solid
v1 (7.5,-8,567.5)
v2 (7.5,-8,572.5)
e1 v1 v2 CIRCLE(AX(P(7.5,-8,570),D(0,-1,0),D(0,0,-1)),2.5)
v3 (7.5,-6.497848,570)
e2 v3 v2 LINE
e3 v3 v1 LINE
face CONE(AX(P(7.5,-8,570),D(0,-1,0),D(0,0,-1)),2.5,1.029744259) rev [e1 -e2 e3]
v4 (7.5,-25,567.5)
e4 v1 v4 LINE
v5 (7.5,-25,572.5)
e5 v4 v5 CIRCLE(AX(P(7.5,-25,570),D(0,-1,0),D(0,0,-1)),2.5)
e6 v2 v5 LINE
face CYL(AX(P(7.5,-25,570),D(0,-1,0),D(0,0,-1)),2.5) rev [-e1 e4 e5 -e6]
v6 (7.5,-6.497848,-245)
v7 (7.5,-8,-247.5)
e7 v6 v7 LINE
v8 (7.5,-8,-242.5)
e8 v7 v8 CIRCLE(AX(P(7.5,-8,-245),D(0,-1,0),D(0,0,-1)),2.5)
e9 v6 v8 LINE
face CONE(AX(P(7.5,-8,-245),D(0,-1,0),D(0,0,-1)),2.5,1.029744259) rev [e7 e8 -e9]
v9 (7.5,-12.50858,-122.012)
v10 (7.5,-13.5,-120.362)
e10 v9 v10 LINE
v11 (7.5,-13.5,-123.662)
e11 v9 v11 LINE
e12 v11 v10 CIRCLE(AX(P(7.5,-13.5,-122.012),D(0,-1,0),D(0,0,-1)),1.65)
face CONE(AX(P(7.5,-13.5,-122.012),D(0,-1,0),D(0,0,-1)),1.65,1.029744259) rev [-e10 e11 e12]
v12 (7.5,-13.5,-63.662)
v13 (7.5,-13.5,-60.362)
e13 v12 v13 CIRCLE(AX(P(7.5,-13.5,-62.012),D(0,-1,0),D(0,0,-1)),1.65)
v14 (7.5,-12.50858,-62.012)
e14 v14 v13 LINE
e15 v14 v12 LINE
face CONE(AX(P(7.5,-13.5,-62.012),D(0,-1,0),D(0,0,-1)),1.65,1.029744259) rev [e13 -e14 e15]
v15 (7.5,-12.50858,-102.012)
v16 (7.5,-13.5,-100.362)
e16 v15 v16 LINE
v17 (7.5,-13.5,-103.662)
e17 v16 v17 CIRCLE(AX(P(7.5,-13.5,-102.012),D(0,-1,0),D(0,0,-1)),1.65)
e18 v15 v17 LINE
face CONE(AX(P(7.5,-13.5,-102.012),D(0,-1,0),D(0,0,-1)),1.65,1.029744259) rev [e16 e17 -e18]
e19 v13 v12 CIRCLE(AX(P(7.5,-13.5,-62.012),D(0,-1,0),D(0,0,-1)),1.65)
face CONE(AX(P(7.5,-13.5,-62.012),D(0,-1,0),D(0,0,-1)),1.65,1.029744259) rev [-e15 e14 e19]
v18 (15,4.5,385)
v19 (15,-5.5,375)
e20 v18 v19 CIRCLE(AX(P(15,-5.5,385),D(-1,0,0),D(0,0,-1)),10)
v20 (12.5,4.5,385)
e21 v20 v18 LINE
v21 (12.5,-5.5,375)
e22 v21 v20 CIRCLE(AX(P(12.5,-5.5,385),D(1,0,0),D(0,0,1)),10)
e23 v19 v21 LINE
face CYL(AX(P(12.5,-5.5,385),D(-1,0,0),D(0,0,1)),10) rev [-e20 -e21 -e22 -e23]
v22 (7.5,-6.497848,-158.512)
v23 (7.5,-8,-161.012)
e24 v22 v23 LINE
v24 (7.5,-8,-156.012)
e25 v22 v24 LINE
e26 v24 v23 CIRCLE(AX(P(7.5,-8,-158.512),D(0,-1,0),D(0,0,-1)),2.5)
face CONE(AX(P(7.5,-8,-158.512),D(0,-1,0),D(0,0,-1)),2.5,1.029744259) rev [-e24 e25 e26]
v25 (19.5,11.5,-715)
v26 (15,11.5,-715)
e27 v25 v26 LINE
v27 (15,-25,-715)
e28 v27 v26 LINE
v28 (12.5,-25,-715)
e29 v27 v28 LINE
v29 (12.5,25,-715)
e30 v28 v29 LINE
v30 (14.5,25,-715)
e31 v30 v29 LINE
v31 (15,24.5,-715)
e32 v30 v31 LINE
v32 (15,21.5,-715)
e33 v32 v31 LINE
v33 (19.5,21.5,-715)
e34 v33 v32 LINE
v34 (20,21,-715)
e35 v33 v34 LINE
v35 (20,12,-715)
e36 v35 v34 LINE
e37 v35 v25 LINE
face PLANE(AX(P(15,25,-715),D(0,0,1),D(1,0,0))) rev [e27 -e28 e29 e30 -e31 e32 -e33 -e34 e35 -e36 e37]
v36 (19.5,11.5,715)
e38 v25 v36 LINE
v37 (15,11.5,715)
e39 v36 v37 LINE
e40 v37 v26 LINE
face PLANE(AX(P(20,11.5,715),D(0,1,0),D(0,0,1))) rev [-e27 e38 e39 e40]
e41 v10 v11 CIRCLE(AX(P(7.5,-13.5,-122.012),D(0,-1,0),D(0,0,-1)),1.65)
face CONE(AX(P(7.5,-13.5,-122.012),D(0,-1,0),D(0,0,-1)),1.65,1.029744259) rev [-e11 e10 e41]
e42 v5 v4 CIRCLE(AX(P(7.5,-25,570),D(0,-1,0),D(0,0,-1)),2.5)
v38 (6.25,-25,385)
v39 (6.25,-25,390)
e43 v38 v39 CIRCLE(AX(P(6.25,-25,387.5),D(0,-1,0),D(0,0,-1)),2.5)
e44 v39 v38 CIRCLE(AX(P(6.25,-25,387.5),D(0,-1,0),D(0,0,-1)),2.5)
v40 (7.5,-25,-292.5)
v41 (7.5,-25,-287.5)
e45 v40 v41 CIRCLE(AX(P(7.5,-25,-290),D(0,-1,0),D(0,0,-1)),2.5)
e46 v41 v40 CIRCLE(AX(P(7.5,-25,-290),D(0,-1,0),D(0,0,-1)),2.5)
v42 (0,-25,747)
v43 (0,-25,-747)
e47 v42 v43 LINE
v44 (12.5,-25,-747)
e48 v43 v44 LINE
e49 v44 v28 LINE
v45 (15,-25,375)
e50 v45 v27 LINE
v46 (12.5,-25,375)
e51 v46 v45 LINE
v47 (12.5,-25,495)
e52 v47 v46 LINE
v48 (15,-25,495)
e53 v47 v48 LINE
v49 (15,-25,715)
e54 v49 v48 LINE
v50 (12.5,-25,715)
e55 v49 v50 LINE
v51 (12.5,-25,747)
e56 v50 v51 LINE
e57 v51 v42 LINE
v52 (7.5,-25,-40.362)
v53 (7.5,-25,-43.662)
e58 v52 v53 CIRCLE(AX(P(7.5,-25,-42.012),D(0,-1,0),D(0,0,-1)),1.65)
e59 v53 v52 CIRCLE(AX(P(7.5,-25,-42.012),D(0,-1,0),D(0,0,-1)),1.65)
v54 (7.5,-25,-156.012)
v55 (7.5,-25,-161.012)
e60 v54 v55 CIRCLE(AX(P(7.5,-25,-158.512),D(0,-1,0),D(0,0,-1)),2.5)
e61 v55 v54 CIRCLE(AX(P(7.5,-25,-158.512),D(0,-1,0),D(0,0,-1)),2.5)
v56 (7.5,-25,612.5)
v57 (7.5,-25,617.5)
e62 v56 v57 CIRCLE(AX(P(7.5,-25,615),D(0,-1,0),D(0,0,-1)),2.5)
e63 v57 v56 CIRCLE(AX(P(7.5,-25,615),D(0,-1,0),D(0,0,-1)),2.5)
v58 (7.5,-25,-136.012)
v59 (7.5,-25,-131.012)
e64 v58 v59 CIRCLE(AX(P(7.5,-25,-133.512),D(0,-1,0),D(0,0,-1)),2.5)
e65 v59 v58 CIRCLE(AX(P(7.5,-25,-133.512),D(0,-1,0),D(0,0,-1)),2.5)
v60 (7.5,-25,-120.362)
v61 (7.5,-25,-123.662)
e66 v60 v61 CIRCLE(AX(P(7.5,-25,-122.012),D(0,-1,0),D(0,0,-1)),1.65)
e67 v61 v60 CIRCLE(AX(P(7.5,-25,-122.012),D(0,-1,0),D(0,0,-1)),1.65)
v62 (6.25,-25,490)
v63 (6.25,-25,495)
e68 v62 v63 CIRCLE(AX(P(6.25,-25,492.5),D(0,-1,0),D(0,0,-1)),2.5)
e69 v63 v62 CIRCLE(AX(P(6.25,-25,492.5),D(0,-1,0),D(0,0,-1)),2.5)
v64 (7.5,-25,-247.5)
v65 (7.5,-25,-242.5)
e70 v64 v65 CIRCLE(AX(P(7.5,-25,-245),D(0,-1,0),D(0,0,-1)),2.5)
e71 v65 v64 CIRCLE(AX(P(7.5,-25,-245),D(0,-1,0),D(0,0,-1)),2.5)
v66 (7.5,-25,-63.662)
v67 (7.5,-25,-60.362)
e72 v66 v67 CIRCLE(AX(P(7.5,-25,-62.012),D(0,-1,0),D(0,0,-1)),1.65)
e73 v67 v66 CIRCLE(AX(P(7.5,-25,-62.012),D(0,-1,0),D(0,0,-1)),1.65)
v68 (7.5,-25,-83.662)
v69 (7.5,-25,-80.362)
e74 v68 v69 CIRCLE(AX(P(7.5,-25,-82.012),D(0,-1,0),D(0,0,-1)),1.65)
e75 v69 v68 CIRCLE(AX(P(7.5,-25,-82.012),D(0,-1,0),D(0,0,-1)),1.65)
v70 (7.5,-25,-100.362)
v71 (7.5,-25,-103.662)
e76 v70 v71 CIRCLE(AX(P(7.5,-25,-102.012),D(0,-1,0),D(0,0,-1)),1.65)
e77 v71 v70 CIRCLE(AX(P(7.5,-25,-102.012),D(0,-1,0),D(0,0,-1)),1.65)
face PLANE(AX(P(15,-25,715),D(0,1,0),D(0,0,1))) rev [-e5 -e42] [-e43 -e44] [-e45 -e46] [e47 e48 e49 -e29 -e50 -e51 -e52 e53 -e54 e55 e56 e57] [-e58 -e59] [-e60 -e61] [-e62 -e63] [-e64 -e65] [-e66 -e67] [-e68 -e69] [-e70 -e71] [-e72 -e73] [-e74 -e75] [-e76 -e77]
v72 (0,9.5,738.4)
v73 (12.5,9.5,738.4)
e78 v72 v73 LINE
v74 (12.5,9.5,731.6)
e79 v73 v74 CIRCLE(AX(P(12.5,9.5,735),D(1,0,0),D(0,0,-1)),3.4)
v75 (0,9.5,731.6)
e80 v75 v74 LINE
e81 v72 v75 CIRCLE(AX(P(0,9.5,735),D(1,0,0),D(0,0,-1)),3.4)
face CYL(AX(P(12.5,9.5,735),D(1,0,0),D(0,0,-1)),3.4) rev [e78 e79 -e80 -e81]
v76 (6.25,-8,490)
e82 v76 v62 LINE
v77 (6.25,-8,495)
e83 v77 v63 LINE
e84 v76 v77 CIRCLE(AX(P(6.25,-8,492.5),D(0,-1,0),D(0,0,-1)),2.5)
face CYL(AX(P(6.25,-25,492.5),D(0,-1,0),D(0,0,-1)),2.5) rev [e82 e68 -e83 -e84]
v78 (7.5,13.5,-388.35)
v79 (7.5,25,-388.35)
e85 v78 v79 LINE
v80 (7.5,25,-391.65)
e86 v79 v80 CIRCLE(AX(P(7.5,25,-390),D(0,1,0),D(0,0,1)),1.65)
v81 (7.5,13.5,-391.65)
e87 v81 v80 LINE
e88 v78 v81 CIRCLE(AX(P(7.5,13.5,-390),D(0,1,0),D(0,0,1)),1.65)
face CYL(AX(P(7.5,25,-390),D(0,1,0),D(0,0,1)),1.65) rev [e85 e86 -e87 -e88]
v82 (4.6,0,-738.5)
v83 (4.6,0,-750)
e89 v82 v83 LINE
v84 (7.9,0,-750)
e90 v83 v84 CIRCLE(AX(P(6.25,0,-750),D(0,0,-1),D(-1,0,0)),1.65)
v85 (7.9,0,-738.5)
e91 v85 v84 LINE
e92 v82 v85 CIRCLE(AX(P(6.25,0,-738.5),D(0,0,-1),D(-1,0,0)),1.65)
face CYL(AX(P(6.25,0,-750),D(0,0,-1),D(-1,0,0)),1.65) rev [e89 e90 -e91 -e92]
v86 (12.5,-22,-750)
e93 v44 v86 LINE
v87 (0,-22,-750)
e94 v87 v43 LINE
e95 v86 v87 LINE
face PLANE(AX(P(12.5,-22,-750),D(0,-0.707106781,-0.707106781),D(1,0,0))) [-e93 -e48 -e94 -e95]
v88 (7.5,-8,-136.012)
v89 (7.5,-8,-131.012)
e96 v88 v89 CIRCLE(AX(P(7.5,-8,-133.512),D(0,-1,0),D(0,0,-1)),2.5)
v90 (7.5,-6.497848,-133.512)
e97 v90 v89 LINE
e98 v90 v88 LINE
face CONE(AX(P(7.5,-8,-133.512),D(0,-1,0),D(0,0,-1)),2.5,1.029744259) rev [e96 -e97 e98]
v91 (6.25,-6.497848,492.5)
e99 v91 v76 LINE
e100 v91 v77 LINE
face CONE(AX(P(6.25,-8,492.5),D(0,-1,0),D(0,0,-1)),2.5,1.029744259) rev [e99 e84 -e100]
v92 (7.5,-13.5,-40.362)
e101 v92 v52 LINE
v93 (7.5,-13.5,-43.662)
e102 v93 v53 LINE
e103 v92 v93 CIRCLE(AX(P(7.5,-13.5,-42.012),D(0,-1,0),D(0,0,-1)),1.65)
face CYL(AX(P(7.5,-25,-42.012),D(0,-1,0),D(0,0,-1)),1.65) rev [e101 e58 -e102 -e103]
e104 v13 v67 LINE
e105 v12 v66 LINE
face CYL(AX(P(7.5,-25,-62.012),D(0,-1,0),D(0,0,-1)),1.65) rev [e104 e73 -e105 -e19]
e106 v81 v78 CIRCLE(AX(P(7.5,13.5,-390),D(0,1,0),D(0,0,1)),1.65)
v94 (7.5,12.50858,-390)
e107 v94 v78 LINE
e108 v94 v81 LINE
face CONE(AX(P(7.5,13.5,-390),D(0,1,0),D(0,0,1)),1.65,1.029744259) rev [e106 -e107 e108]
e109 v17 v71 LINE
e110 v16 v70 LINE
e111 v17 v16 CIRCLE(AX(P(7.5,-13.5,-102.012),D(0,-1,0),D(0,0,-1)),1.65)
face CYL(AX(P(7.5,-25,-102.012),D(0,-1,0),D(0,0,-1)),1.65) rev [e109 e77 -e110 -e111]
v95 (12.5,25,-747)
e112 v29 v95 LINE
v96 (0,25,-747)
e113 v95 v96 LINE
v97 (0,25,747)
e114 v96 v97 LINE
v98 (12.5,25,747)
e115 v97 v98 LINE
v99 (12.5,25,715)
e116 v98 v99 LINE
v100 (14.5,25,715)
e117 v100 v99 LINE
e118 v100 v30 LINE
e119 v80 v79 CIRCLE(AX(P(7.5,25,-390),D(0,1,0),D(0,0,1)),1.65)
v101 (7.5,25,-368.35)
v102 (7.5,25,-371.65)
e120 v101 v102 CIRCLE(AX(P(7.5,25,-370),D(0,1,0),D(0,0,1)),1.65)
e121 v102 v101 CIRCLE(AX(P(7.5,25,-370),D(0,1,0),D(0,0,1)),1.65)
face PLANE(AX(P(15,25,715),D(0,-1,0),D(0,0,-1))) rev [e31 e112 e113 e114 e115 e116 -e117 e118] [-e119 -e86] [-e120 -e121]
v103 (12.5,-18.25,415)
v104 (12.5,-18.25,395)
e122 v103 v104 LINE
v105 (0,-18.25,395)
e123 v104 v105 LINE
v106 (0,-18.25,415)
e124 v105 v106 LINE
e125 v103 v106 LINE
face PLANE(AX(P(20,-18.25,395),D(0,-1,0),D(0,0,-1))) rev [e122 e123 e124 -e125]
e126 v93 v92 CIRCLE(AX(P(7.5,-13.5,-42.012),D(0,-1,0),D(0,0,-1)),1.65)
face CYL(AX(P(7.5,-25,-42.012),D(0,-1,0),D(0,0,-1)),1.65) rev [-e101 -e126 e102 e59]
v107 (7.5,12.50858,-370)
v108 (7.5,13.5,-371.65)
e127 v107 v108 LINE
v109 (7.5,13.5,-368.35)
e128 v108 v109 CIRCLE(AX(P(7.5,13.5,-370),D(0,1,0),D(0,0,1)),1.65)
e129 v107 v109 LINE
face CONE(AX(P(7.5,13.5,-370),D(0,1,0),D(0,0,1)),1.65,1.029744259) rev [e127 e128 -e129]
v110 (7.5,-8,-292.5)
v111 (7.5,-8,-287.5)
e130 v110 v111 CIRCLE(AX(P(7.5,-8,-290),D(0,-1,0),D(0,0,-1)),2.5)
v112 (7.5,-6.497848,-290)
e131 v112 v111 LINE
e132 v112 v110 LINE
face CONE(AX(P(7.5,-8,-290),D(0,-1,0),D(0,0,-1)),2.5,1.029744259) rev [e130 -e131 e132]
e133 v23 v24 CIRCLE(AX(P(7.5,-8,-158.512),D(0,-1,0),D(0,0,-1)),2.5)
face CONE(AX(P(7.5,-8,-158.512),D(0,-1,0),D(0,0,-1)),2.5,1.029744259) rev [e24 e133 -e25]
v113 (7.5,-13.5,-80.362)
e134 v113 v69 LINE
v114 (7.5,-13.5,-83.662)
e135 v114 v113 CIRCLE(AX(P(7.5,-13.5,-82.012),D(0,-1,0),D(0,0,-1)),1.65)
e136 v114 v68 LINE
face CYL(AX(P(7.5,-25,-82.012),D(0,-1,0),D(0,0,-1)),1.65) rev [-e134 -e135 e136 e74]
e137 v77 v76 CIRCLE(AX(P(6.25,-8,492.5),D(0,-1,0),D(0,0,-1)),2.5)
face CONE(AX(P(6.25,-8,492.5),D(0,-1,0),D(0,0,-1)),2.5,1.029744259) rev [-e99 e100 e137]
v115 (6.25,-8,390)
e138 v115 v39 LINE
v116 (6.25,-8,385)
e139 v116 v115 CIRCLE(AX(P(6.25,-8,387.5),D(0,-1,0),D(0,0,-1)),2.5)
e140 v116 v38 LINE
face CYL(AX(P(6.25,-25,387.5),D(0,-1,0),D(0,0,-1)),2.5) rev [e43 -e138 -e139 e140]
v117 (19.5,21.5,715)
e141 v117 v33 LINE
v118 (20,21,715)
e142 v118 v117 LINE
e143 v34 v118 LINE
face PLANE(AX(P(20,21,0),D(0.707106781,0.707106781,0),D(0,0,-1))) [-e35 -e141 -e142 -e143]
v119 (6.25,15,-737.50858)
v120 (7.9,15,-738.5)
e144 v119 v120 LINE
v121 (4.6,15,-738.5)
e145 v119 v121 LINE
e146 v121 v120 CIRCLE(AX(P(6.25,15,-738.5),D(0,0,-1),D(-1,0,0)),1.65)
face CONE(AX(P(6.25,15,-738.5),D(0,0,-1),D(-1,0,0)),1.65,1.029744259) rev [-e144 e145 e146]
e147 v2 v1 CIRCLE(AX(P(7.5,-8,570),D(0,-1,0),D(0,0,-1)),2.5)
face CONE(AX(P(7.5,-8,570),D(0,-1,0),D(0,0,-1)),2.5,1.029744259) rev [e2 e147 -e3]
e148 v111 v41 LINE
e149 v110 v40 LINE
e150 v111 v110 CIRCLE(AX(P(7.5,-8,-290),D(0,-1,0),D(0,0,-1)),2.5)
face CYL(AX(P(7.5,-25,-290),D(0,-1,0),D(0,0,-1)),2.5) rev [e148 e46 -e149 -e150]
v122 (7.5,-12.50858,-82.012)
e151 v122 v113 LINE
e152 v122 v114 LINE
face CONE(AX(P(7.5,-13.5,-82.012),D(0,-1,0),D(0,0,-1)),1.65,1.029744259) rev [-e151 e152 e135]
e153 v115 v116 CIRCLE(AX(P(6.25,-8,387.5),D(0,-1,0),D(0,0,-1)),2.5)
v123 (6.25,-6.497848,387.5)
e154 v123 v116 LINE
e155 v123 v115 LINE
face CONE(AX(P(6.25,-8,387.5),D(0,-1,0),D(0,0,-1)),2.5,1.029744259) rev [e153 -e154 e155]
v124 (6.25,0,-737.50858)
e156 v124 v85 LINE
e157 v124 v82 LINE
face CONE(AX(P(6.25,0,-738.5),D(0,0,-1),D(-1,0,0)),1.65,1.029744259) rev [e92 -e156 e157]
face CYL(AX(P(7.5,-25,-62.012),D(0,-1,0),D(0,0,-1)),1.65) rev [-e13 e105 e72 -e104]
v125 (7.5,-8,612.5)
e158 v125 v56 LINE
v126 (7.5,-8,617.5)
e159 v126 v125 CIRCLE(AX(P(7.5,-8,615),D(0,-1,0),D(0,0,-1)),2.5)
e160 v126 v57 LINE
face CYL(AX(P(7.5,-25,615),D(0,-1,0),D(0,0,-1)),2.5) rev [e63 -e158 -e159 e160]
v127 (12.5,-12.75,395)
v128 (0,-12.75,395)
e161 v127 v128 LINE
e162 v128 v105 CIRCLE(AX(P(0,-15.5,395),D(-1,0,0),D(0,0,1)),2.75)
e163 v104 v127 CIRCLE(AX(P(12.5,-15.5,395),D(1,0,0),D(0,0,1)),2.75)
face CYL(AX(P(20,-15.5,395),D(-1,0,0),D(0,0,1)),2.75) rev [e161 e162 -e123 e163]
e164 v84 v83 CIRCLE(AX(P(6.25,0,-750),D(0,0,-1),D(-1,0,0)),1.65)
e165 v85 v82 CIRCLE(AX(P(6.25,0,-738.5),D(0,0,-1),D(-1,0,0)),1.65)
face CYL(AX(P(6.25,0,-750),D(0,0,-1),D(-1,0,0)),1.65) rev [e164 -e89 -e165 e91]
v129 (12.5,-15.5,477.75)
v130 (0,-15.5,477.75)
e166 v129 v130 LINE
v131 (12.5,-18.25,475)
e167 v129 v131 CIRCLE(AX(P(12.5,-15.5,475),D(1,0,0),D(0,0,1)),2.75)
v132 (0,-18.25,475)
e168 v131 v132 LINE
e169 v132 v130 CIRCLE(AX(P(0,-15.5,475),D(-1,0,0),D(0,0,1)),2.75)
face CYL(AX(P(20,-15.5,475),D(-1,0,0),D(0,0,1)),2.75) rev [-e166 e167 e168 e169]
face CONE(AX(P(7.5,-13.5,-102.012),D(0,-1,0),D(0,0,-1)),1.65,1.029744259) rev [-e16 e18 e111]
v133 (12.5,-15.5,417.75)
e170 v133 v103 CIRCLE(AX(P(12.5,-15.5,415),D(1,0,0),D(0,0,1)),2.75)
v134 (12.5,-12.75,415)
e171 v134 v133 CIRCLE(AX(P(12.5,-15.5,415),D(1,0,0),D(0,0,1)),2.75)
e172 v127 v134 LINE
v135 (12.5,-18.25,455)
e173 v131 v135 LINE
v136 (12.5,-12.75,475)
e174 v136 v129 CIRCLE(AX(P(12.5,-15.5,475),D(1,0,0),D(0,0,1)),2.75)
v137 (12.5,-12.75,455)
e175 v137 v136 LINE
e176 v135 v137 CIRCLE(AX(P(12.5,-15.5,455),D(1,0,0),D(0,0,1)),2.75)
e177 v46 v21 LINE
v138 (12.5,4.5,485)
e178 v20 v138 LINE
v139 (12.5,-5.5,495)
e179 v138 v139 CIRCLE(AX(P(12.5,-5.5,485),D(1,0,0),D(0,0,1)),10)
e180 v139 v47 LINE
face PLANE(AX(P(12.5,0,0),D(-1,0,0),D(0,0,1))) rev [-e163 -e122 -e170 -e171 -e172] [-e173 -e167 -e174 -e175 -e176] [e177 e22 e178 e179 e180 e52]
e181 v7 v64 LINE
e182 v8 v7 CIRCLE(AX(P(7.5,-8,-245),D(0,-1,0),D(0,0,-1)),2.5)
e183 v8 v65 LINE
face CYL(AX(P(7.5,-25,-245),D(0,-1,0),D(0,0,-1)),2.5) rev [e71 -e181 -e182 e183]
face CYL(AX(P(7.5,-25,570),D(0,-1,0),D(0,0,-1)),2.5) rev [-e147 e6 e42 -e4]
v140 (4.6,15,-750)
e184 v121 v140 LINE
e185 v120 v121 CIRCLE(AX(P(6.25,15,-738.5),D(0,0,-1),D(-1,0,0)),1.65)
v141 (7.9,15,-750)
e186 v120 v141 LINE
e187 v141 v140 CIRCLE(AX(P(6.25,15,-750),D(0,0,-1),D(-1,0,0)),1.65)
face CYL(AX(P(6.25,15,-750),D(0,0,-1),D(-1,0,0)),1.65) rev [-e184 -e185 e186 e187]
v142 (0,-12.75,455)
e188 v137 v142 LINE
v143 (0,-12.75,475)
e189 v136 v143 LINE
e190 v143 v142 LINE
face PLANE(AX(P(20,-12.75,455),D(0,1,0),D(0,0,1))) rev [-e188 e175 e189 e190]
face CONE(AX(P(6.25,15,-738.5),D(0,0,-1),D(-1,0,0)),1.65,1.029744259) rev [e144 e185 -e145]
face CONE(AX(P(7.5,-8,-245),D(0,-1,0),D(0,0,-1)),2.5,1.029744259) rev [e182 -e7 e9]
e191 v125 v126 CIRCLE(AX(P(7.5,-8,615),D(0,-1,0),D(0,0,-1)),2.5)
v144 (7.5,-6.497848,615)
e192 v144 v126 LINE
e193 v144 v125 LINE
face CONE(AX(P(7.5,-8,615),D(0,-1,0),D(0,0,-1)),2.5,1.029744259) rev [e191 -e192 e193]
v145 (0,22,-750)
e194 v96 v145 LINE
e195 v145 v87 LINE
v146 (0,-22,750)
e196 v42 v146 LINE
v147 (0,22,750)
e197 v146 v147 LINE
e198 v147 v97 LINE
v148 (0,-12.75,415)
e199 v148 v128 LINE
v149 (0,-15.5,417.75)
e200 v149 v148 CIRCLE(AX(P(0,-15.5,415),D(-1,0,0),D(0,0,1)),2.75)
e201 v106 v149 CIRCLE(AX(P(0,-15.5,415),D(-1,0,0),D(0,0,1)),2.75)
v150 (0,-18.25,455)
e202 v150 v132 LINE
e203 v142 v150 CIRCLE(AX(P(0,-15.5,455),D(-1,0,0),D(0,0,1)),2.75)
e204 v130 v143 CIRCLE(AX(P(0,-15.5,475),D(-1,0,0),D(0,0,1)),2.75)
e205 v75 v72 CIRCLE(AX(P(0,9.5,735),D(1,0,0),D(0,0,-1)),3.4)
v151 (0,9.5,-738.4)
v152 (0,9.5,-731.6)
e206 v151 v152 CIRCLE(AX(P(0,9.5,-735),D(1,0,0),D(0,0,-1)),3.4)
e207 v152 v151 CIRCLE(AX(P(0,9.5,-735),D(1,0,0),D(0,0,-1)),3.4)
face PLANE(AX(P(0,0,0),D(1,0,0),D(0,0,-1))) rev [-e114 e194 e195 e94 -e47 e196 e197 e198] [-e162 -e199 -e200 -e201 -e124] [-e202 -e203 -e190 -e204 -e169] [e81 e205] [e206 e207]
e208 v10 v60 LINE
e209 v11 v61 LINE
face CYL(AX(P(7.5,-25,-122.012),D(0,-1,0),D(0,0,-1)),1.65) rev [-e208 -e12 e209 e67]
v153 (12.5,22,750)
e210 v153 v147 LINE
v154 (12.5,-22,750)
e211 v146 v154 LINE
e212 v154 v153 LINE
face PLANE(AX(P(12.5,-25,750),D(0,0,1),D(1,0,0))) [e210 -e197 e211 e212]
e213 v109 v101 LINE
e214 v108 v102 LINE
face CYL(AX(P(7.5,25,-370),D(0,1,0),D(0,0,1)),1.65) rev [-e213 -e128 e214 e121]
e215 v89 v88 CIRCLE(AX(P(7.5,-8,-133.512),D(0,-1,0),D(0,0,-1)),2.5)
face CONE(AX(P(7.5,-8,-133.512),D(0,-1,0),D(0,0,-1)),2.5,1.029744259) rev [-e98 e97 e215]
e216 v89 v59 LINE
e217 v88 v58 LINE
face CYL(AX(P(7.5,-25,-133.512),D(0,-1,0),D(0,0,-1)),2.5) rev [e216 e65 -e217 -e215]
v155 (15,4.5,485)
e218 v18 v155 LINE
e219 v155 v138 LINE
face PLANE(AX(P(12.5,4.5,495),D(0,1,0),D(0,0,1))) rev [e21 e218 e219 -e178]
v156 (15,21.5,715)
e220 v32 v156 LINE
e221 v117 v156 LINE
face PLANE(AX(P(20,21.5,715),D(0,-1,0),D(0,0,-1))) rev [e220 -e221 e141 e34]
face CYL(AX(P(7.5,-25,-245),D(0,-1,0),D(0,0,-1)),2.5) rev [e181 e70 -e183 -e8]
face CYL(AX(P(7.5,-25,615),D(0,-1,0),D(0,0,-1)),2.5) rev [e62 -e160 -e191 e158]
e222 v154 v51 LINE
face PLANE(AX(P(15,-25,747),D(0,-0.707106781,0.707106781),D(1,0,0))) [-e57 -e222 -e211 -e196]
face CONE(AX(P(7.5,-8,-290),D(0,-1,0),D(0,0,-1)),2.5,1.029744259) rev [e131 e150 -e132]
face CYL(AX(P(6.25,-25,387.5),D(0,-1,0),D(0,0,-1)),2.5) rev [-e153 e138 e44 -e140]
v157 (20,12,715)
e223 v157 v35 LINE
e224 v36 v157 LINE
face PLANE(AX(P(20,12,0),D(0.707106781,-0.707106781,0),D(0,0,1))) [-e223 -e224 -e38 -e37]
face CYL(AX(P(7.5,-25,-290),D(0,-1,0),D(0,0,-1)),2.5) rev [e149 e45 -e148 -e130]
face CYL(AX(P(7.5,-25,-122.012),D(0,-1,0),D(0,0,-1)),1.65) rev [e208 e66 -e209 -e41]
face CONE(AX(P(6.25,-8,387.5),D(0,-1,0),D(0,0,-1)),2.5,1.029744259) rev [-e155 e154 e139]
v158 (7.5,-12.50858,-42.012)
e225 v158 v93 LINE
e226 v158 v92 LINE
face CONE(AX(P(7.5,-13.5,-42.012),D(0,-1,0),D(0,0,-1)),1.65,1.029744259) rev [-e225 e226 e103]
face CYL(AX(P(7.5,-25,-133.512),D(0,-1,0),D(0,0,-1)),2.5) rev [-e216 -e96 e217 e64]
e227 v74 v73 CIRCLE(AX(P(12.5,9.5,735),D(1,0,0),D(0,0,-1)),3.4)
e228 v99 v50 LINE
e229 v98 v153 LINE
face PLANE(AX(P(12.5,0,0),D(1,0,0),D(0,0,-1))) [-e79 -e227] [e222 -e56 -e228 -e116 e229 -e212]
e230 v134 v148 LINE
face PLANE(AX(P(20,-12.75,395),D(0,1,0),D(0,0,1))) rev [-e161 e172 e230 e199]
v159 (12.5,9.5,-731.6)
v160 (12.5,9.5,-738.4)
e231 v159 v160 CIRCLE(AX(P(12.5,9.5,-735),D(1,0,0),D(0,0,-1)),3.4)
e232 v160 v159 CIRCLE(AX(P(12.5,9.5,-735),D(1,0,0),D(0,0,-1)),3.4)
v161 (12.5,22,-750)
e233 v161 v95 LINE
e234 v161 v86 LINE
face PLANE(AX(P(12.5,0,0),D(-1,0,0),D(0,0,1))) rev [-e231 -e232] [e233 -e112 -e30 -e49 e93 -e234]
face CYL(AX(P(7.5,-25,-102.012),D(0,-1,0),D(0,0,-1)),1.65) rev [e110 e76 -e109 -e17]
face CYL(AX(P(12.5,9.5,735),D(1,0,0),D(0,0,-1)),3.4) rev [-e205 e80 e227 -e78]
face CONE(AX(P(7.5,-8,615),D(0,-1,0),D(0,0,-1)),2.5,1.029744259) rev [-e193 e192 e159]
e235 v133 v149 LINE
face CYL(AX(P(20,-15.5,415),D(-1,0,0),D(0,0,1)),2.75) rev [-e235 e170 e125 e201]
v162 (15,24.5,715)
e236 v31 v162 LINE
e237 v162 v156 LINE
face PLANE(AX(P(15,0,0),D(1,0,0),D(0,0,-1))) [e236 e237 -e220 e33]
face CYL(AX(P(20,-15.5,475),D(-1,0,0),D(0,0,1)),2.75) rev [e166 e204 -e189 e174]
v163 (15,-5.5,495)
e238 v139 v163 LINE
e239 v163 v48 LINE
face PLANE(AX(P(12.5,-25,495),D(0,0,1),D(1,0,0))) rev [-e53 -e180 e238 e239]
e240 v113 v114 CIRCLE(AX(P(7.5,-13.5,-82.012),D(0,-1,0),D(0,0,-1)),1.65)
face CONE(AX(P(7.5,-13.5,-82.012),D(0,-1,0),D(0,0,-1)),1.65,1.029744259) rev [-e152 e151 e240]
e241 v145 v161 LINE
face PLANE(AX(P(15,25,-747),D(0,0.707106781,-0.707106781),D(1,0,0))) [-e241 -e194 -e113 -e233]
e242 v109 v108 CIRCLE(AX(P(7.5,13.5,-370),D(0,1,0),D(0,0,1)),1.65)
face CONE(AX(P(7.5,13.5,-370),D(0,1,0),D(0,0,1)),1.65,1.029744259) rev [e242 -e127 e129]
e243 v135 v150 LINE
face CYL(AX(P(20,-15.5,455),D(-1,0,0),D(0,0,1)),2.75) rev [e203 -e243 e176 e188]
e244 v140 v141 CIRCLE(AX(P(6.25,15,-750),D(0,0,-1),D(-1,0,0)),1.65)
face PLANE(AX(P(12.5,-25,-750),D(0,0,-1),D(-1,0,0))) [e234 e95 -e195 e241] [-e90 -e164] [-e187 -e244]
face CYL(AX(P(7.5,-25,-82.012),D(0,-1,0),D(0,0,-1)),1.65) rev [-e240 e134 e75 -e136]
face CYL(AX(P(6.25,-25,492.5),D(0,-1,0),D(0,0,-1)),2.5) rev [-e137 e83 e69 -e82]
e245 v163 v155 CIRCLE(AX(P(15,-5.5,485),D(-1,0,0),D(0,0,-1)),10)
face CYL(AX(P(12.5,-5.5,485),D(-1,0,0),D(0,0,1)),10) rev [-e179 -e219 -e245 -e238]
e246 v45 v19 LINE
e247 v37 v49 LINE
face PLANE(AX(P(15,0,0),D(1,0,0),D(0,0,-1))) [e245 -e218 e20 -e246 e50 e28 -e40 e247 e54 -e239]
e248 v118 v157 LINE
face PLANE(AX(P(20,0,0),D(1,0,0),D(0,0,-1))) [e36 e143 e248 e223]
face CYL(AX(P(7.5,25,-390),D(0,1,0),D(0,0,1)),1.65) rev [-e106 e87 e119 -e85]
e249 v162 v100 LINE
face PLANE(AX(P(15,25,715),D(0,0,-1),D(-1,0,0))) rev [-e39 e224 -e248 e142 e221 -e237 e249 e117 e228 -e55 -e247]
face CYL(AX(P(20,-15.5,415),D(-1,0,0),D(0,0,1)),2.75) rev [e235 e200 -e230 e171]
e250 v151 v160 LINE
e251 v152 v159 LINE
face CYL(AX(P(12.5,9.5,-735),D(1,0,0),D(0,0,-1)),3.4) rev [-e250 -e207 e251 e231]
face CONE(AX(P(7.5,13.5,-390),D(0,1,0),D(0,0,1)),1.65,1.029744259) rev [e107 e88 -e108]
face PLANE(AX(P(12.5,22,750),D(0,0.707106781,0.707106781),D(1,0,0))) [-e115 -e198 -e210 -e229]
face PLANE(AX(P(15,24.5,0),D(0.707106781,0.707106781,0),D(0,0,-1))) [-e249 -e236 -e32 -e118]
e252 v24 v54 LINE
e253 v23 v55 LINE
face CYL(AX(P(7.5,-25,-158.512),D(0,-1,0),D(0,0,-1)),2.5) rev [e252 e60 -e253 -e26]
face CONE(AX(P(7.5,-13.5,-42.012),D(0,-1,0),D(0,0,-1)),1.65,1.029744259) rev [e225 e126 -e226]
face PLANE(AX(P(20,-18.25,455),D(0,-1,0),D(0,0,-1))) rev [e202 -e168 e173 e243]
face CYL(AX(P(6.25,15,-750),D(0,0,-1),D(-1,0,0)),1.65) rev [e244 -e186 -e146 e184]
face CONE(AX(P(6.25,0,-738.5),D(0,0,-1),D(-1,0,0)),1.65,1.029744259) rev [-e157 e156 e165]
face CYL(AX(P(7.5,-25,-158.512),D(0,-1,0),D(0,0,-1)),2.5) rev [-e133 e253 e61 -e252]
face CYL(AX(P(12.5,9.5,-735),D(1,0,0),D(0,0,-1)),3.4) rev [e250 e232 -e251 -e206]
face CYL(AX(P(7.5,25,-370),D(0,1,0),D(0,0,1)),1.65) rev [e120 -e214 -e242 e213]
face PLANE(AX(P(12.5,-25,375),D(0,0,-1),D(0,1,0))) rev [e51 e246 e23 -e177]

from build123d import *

# Parameters (mm, degrees)
SKETCH_1_W             = 1430
SKETCH_1_H             = 50
EXTRUDE_1_DEPTH        = 15
SKETCH_5_W             = 1430
SKETCH_5_H             = 10
EXTRUDE_3_DEPTH        = 5
HOLE_WIZARD_M6_2_D     = 5
HOLE_WIZARD_M6_2_DEPTH = 17
HOLE_WIZARD_M6_2_TIP   = 1.502151548
CHAMFER_2_SIZE         = 0.5
SKETCH_10_W            = 35
SKETCH_10_H            = 50
EXTRUDE_4_DEPTH        = 12.5
HOLE_WIZARD_M8_1_D     = 6.8
CHAMFER_3_SIZE         = 3
CUT_EXTRUDE_1_DEPTH    = 751.68302232
SKETCH_14_W            = 120
SKETCH_14_H            = 29.5
CUT_EXTRUDE_2_DEPTH    = 2.5
FILLET_1_R             = 10
HOLE_WIZARD_M6_3_D     = 5
HOLE_WIZARD_M6_3_DEPTH = 17
HOLE_WIZARD_M6_3_TIP   = 1.502151548
HOLE_WIZARD_M6_5_D     = 5
HOLE_WIZARD_M6_5_DEPTH = 17
HOLE_WIZARD_M6_5_TIP   = 1.502151548
HOLE_WIZARD_M4_1_D     = 3.3
HOLE_WIZARD_M4_1_DEPTH = 11.5
HOLE_WIZARD_M4_1_TIP   = 0.991420021
HOLE_WIZARD_M4_2_D     = 3.3
HOLE_WIZARD_M4_2_DEPTH = 11.5
HOLE_WIZARD_M4_2_TIP   = 0.991420021
HOLE_WIZARD_M4_3_D     = 3.3
HOLE_WIZARD_M4_3_DEPTH = 11.5
HOLE_WIZARD_M4_3_TIP   = 0.991420021


with BuildPart() as part:
    # 草图1 → 凸台-拉伸1 (new body)
    with BuildSketch(Plane(origin=(0, 0, 0), x_dir=(0, 0, -1), z_dir=(1, 0, 0))):
        Rectangle(SKETCH_1_W, SKETCH_1_H)
    extrude(amount=EXTRUDE_1_DEPTH)

    # 草图5 → 凸台-拉伸3 (add)
    with BuildSketch(Plane(origin=(15, 0, 0), x_dir=(0, 0, -1), z_dir=(1, 0, 0))):
        with Locations((0, 16.5)):
            Rectangle(SKETCH_5_W, SKETCH_5_H)
    extrude(amount=EXTRUDE_3_DEPTH)

    # M6 螺纹孔2
    with Locations(Plane(origin=(-9.706715775, -25, 33.268833901), x_dir=(0, 0, -1), z_dir=(0, -1, 0))):
        with Locations((-581.731166099, 17.206715775), (-536.731166099, 17.206715775), (323.268833901, 17.206715775), (278.268833901, 17.206715775)):
            Hole(HOLE_WIZARD_M6_2_D / 2, depth=HOLE_WIZARD_M6_2_DEPTH)
            with Locations((0, 0, -(HOLE_WIZARD_M6_2_DEPTH + HOLE_WIZARD_M6_2_TIP / 2))):  # 118° drill point
                Cone(0, HOLE_WIZARD_M6_2_D / 2, HOLE_WIZARD_M6_2_TIP, mode=Mode.SUBTRACT)

    # 倒角2
    chamfer_2_edges = [part.edges().sort_by_distance(p)[0] for p in [
        (15, 25, 0),
        (20, 21.5, 0),
        (20, 11.5, 0),
    ]]
    chamfer(chamfer_2_edges, length=CHAMFER_2_SIZE)

    # 草图10 → 凸台-拉伸4 (add)
    with BuildSketch(Plane.ZY):
        with Locations((-732.5, 0)):
            Rectangle(SKETCH_10_W, SKETCH_10_H)
        with Locations((732.5, 0)):
            Rectangle(SKETCH_10_W, SKETCH_10_H)
    extrude(amount=-EXTRUDE_4_DEPTH)

    # M8 螺纹孔1 (through all)
    with Locations(Plane(origin=(12.5, 0, 0), x_dir=(0, 0, -1), z_dir=(1, 0, 0))):
        with Locations((-735, 9.5), (735, 9.5)):
            Hole(HOLE_WIZARD_M8_1_D / 2)

    # 倒角3
    chamfer_3_edges = [part.edges().sort_by_distance(p)[0] for p in [
        (6.25, -25, -750),
        (6.25, 25, -750),
        (6.25, -25, 750),
        (6.25, 25, 750),
    ]]
    chamfer(chamfer_3_edges, length=CHAMFER_3_SIZE)

    # 草图13 → 切除-拉伸1 (cut, through all)
    with BuildSketch(Plane.ZY):
        with BuildLine():
            Line((395, -12.75), (415, -12.75))
            ThreePointArc((415, -12.75), (417.75, -15.5), (415, -18.25))
            Line((415, -18.25), (395, -18.25))
            ThreePointArc((395, -18.25), (392.25, -15.5), (395, -12.75))
        make_face()
        with BuildLine():
            Line((455, -12.75), (475, -12.75))
            ThreePointArc((475, -12.75), (477.75, -15.5), (475, -18.25))
            Line((475, -18.25), (455, -18.25))
            ThreePointArc((455, -18.25), (452.25, -15.5), (455, -12.75))
        make_face()
    extrude(amount=-CUT_EXTRUDE_1_DEPTH, mode=Mode.SUBTRACT)

    # 草图14 → 切除-拉伸2 (cut)
    with BuildSketch(Plane(origin=(15, 0, 0), x_dir=(0, 0, -1), z_dir=(1, 0, 0))):
        with Locations((-435, -10.25)):
            Rectangle(SKETCH_14_W, SKETCH_14_H)
    extrude(amount=-CUT_EXTRUDE_2_DEPTH, mode=Mode.SUBTRACT)

    # 圆角1
    fillet_1_edges = [part.edges().sort_by_distance(p)[0] for p in [
        (13.75, 4.5, 495),
        (13.75, 4.5, 375),
    ]]
    fillet(fillet_1_edges, radius=FILLET_1_R)

    # M6 螺纹孔3
    with Locations(Plane(origin=(0, -25, 0), x_dir=(-1, 0, 0), z_dir=(0, -1, 0))):
        with Locations((-7.5, 133.512), (-7.5, 158.512)):
            Hole(HOLE_WIZARD_M6_3_D / 2, depth=HOLE_WIZARD_M6_3_DEPTH)
            with Locations((0, 0, -(HOLE_WIZARD_M6_3_DEPTH + HOLE_WIZARD_M6_3_TIP / 2))):  # 118° drill point
                Cone(0, HOLE_WIZARD_M6_3_D / 2, HOLE_WIZARD_M6_3_TIP, mode=Mode.SUBTRACT)

    # M6 螺纹孔5
    with Locations(Plane(origin=(0, -25, 0), x_dir=(-1, 0, 0), z_dir=(0, -1, 0))):
        with Locations((-6.25, -492.5), (-6.25, -387.5)):
            Hole(HOLE_WIZARD_M6_5_D / 2, depth=HOLE_WIZARD_M6_5_DEPTH)
            with Locations((0, 0, -(HOLE_WIZARD_M6_5_DEPTH + HOLE_WIZARD_M6_5_TIP / 2))):  # 118° drill point
                Cone(0, HOLE_WIZARD_M6_5_D / 2, HOLE_WIZARD_M6_5_TIP, mode=Mode.SUBTRACT)

    # M4 螺纹孔1
    with Locations(Plane(origin=(0, 0, -750), x_dir=(-1, 0, 0), z_dir=(0, 0, -1))):
        with Locations((-6.25, 15), (-6.25, 0)):
            Hole(HOLE_WIZARD_M4_1_D / 2, depth=HOLE_WIZARD_M4_1_DEPTH)
            with Locations((0, 0, -(HOLE_WIZARD_M4_1_DEPTH + HOLE_WIZARD_M4_1_TIP / 2))):  # 118° drill point
                Cone(0, HOLE_WIZARD_M4_1_D / 2, HOLE_WIZARD_M4_1_TIP, mode=Mode.SUBTRACT)

    # M4 螺纹孔2
    with Locations(Plane(origin=(0, 25, 0), x_dir=(1, 0, 0), z_dir=(0, 1, 0))):
        with Locations((7.5, 390), (7.5, 370)):
            Hole(HOLE_WIZARD_M4_2_D / 2, depth=HOLE_WIZARD_M4_2_DEPTH)
            with Locations((0, 0, -(HOLE_WIZARD_M4_2_DEPTH + HOLE_WIZARD_M4_2_TIP / 2))):  # 118° drill point
                Cone(0, HOLE_WIZARD_M4_2_D / 2, HOLE_WIZARD_M4_2_TIP, mode=Mode.SUBTRACT)

    # M4 螺纹孔3
    with Locations(Plane(origin=(0, -25, 0), x_dir=(-1, 0, 0), z_dir=(0, -1, 0))):
        with Locations((-7.5, 122.012), (-7.5, 102.012), (-7.5, 82.012), (-7.5, 62.012), (-7.5, 42.012)):
            Hole(HOLE_WIZARD_M4_3_D / 2, depth=HOLE_WIZARD_M4_3_DEPTH)
            with Locations((0, 0, -(HOLE_WIZARD_M4_3_DEPTH + HOLE_WIZARD_M4_3_TIP / 2))):  # 118° drill point
                Cone(0, HOLE_WIZARD_M4_3_D / 2, HOLE_WIZARD_M4_3_TIP, mode=Mode.SUBTRACT)


solid = part.part
